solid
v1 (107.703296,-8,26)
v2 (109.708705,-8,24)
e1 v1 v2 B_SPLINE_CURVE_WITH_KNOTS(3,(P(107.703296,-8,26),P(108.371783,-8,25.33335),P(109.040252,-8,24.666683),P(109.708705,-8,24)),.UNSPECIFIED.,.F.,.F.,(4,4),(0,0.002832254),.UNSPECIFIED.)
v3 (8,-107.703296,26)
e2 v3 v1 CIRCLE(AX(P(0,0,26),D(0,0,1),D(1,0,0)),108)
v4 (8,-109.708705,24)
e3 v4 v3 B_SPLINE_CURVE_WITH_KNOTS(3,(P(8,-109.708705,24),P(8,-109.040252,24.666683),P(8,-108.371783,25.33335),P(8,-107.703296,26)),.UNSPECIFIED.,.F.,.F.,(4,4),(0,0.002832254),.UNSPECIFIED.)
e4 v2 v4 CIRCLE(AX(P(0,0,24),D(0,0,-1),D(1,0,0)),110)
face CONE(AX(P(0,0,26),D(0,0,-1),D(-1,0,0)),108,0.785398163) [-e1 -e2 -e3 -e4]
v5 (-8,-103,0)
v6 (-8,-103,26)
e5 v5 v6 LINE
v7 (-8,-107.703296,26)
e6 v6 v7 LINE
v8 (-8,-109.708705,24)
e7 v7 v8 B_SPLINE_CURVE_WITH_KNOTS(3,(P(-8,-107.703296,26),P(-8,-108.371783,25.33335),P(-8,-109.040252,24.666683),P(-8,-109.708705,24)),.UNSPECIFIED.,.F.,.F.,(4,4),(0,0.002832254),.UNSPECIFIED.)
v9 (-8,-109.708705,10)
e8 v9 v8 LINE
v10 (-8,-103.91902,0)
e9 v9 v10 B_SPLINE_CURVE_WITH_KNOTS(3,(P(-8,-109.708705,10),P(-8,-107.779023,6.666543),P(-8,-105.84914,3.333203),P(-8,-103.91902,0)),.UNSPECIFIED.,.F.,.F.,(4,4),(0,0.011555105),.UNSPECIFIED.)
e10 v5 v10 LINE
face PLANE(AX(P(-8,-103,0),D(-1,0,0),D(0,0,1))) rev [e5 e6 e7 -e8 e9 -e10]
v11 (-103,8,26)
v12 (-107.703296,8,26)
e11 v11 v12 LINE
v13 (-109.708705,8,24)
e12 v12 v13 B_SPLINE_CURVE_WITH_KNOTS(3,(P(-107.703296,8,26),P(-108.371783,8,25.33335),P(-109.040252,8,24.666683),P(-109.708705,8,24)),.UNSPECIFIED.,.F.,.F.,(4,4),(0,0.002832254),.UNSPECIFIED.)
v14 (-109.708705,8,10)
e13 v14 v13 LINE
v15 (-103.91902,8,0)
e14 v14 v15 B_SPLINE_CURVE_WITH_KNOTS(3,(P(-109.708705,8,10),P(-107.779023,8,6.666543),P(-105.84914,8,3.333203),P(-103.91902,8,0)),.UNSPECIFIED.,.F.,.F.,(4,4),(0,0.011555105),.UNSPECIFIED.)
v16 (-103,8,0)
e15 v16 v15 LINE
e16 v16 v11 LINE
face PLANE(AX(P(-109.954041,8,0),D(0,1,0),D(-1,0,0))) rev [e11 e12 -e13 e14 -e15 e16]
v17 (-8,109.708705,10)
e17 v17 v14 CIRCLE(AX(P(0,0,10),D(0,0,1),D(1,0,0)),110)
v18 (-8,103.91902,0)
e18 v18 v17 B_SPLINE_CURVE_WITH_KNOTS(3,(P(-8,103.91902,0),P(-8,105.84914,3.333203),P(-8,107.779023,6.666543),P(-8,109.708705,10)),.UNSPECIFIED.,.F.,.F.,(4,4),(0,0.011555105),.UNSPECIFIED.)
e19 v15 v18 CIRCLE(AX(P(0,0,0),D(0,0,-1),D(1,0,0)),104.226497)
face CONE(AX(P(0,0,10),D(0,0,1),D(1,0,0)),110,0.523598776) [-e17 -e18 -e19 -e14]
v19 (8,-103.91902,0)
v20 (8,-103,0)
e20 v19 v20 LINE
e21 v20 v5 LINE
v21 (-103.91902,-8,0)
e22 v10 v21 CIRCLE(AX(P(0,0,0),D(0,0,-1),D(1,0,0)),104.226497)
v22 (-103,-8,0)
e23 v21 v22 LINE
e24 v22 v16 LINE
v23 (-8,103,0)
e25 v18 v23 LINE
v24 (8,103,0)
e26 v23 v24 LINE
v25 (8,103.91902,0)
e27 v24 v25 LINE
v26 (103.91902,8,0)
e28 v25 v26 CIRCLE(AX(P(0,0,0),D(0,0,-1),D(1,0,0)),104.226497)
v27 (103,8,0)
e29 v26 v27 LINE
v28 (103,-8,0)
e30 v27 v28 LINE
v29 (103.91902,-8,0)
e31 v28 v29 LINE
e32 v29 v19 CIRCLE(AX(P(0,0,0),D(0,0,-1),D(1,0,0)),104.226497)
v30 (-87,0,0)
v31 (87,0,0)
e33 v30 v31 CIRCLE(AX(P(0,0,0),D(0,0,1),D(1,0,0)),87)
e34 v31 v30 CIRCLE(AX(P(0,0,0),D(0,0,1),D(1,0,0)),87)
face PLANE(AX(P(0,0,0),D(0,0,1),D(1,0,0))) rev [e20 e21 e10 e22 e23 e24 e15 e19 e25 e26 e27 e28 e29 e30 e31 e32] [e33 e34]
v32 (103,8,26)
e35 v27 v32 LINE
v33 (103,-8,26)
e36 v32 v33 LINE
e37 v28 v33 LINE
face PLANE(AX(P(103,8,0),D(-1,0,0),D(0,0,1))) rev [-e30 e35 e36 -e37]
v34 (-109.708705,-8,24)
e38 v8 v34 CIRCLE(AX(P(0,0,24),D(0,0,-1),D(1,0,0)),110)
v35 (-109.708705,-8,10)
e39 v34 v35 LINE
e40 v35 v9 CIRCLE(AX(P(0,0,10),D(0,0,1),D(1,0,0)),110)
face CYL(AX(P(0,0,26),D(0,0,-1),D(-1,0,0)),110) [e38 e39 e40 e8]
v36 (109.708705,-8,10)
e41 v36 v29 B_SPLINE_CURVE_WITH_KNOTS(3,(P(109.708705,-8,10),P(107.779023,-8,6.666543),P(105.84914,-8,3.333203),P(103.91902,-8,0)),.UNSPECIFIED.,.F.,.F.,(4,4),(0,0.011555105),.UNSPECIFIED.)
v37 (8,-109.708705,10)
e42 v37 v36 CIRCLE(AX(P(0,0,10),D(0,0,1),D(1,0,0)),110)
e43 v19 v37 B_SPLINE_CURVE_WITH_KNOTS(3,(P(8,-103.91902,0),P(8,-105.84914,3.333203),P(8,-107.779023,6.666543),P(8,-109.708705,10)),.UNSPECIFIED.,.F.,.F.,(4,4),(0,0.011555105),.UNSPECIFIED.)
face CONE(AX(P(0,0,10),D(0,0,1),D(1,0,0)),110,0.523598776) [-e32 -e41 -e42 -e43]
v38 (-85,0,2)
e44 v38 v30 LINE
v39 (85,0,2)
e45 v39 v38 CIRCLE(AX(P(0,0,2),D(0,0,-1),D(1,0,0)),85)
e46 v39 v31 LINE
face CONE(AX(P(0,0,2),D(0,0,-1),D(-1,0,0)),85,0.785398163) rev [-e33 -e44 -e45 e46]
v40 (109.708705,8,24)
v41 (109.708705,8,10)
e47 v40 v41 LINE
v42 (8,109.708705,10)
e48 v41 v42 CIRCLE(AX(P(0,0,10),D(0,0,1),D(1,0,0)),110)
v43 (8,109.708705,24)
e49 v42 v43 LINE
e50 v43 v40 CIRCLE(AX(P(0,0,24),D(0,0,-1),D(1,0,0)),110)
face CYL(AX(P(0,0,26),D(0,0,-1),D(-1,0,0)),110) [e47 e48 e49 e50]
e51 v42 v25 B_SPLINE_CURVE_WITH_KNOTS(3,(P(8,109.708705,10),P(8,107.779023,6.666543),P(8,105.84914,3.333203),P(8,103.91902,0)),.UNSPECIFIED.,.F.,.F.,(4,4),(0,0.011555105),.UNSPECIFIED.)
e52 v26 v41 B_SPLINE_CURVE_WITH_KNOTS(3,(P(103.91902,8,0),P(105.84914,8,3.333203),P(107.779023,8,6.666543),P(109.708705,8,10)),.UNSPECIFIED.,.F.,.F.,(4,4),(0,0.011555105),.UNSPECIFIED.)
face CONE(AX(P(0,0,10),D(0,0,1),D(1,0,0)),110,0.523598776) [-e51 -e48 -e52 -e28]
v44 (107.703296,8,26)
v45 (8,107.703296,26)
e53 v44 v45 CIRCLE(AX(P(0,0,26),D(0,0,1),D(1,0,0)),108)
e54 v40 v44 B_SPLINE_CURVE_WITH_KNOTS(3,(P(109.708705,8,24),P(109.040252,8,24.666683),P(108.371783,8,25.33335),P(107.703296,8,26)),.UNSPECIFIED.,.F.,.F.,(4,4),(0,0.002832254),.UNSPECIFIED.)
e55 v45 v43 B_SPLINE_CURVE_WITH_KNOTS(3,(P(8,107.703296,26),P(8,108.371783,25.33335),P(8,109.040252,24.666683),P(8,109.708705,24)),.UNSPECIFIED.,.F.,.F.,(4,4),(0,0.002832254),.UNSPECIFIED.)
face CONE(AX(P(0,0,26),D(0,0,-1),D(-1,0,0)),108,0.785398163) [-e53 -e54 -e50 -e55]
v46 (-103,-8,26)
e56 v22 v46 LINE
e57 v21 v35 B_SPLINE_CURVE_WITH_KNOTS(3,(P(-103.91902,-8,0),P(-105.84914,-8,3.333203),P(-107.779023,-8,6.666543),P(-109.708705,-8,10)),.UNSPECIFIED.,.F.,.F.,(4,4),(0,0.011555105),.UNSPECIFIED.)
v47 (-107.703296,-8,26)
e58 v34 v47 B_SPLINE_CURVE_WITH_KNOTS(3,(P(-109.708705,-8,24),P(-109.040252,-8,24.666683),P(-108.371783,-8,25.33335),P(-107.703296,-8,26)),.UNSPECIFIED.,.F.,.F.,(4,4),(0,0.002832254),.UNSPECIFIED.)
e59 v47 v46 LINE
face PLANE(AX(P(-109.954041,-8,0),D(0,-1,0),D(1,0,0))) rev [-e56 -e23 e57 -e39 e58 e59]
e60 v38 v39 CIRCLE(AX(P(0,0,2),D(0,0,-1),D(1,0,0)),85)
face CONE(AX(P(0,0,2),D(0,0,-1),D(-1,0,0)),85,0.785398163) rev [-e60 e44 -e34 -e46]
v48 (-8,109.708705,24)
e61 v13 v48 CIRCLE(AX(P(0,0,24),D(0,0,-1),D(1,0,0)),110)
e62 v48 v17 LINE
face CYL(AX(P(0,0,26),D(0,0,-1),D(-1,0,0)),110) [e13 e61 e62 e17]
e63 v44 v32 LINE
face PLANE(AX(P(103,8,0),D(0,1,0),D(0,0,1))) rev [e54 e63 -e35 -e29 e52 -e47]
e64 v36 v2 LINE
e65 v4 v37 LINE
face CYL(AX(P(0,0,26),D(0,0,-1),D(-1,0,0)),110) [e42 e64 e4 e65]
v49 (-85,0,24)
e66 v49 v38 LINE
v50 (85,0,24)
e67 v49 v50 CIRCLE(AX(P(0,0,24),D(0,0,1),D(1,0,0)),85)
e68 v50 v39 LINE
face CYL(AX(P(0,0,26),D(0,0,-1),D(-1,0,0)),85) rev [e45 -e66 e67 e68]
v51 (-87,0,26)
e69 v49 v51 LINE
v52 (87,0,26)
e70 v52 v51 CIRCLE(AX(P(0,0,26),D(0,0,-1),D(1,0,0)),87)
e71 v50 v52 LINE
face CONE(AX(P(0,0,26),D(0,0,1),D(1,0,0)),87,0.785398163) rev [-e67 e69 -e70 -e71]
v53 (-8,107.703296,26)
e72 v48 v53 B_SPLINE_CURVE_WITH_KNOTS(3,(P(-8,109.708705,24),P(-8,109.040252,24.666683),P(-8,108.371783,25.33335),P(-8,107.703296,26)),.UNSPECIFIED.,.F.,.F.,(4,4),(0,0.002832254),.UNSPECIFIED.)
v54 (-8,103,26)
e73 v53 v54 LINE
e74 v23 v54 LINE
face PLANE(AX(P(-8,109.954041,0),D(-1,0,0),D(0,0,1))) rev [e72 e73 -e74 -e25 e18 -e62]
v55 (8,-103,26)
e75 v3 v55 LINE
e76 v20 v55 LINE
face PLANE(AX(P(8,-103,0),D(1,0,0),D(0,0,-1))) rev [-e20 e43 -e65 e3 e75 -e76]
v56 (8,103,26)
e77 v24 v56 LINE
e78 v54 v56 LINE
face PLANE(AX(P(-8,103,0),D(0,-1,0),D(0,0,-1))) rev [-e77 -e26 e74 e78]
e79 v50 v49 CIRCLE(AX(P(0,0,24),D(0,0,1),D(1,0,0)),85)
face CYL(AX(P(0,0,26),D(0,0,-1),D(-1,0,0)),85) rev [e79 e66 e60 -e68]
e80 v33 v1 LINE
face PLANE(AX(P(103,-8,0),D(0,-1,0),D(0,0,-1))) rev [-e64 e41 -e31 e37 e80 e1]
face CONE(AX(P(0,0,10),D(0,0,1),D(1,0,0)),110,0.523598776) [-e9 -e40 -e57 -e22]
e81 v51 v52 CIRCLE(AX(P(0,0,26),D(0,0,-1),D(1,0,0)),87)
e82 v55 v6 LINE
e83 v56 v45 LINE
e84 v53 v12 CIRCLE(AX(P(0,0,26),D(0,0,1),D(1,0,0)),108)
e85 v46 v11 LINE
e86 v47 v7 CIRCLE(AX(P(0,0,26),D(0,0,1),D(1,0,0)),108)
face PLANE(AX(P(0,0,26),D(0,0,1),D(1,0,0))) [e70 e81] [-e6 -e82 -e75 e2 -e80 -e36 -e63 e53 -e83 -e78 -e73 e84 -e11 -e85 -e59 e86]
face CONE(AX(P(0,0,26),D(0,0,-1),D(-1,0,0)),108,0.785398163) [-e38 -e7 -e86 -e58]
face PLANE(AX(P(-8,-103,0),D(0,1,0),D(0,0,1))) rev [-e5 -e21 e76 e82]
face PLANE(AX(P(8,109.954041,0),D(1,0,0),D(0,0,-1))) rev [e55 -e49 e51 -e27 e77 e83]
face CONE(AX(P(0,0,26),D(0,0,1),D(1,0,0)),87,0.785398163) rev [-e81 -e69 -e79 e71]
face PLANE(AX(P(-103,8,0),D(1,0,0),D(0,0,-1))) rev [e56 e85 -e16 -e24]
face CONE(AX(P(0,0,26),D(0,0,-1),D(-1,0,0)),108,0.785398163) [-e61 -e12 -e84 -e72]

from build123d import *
from OCP.BRepFilletAPI import BRepFilletAPI_MakeChamfer

# Parameters (mm, degrees)
SKETCH2_R           = 110
BOSS_EXTRUDE1_DEPTH = 26
CUT_EXTRUDE1_DEPTH  = 26
CHAMFER1_SIZE       = 2
CHAMFER2_SIZE       = 10
CHAMFER2_SIZE2      = 5.773502692
SKETCH4_R           = 85
CUT_EXTRUDE2_DEPTH  = 26
CHAMFER3_SIZE       = 2


with BuildPart() as part:
    # Sketch2 → Boss-Extrude1 (new body)
    with BuildSketch(Plane.XY):
        with Locations(Location((0, 0, 0), (0, 0, 180))):
            Circle(SKETCH2_R)
    extrude(amount=BOSS_EXTRUDE1_DEPTH)

    # Sketch3 → Cut-Extrude1 (cut)
    with BuildSketch(Plane.XY.offset(26)):
        with BuildLine():
            Line((-8, 109.954040528), (-8, 103))
            Line((-8, 103), (8, 103))
            Line((8, 103), (8, 109.954040528))
            ThreePointArc((8, 109.954040528), (0, 110.244687076), (-8, 109.954040528))
        make_face()
        with BuildLine():
            Line((-109.954040528, -8), (-103, -8))
            Line((-103, -8), (-103, 8))
            Line((-103, 8), (-109.954040528, 8))
            ThreePointArc((-109.954040528, 8), (-110.244687076, 0), (-109.954040528, -8))
        make_face()
        with BuildLine():
            Line((103, 8), (103, -8))
            Line((103, -8), (109.954040528, -8))
            ThreePointArc((109.954040528, -8), (110.244687076, 0), (109.954040528, 8))
            Line((109.954040528, 8), (103, 8))
        make_face()
        with BuildLine():
            Line((-8, -103), (-8, -109.954040528))
            ThreePointArc((-8, -109.954040528), (0, -110.244687076), (8, -109.954040528))
            Line((8, -109.954040528), (8, -103))
            Line((8, -103), (-8, -103))
        make_face()
    extrude(amount=-CUT_EXTRUDE1_DEPTH, mode=Mode.SUBTRACT)

    # Chamfer1
    chamfer1_edges = [part.edges().sort_by_distance(p)[0] for p in [
        (-77.781745931, 77.781745931, 26),
        (77.781745931, 77.781745931, 26),
        (-77.781745931, -77.781745931, 26),
        (77.781745931, -77.781745931, 26),
    ]]
    chamfer(chamfer1_edges, length=CHAMFER1_SIZE)

    # Chamfer2: one chamfer whose edges measure the first distance from different faces: ONE call of the kernel's chamfer builder (chamfer() names one face for all edges)
    chamfer2_edges_1 = [part.edges().sort_by_distance(p)[0] for p in [
        (77.781745931, 77.781745931, 0),
    ]]
    chamfer2_side_1 = [part.faces().sort_by_distance(p)[0] for p in [
        (77.781745931, 77.781745931, 12),
    ]]
    chamfer2_edges_2 = [part.edges().sort_by_distance(p)[0] for p in [
        (-77.781745931, 77.781745931, 0),
    ]]
    chamfer2_side_2 = [part.faces().sort_by_distance(p)[0] for p in [
        (-77.781745931, 77.781745931, 12),
    ]]
    chamfer2_edges_3 = [part.edges().sort_by_distance(p)[0] for p in [
        (-77.781745931, -77.781745931, 0),
    ]]
    chamfer2_side_3 = [part.faces().sort_by_distance(p)[0] for p in [
        (-77.781745931, -77.781745931, 12),
    ]]
    chamfer2_edges_4 = [part.edges().sort_by_distance(p)[0] for p in [
        (77.781745931, -77.781745931, 0),
    ]]
    chamfer2_side_4 = [part.faces().sort_by_distance(p)[0] for p in [
        (77.781745931, -77.781745931, 12),
    ]]
    chamfer2 = BRepFilletAPI_MakeChamfer(part.part.solid().wrapped)
    for e in chamfer2_edges_1:
        chamfer2.Add(CHAMFER2_SIZE, CHAMFER2_SIZE2, e.wrapped, chamfer2_side_1[0].wrapped)  # the first distance lies on this face
    for e in chamfer2_edges_2:
        chamfer2.Add(CHAMFER2_SIZE, CHAMFER2_SIZE2, e.wrapped, chamfer2_side_2[0].wrapped)  # the first distance lies on this face
    for e in chamfer2_edges_3:
        chamfer2.Add(CHAMFER2_SIZE, CHAMFER2_SIZE2, e.wrapped, chamfer2_side_3[0].wrapped)  # the first distance lies on this face
    for e in chamfer2_edges_4:
        chamfer2.Add(CHAMFER2_SIZE, CHAMFER2_SIZE2, e.wrapped, chamfer2_side_4[0].wrapped)  # the first distance lies on this face
    add(Compound.cast(chamfer2.Shape()), mode=Mode.REPLACE)

    # Sketch4 → Cut-Extrude2 (cut)
    with BuildSketch(Plane(origin=(0, 0, 0), x_dir=(-1, 0, 0), z_dir=(0, 0, -1))):
        Circle(SKETCH4_R)
    extrude(amount=-CUT_EXTRUDE2_DEPTH, mode=Mode.SUBTRACT)

    # Chamfer3
    chamfer3_edges = [part.edges().sort_by_distance(p)[0] for p in [
        (85, 0, 26),
        (85, 0, 0),
    ]]
    chamfer(chamfer3_edges, length=CHAMFER3_SIZE)


solid = part.part
